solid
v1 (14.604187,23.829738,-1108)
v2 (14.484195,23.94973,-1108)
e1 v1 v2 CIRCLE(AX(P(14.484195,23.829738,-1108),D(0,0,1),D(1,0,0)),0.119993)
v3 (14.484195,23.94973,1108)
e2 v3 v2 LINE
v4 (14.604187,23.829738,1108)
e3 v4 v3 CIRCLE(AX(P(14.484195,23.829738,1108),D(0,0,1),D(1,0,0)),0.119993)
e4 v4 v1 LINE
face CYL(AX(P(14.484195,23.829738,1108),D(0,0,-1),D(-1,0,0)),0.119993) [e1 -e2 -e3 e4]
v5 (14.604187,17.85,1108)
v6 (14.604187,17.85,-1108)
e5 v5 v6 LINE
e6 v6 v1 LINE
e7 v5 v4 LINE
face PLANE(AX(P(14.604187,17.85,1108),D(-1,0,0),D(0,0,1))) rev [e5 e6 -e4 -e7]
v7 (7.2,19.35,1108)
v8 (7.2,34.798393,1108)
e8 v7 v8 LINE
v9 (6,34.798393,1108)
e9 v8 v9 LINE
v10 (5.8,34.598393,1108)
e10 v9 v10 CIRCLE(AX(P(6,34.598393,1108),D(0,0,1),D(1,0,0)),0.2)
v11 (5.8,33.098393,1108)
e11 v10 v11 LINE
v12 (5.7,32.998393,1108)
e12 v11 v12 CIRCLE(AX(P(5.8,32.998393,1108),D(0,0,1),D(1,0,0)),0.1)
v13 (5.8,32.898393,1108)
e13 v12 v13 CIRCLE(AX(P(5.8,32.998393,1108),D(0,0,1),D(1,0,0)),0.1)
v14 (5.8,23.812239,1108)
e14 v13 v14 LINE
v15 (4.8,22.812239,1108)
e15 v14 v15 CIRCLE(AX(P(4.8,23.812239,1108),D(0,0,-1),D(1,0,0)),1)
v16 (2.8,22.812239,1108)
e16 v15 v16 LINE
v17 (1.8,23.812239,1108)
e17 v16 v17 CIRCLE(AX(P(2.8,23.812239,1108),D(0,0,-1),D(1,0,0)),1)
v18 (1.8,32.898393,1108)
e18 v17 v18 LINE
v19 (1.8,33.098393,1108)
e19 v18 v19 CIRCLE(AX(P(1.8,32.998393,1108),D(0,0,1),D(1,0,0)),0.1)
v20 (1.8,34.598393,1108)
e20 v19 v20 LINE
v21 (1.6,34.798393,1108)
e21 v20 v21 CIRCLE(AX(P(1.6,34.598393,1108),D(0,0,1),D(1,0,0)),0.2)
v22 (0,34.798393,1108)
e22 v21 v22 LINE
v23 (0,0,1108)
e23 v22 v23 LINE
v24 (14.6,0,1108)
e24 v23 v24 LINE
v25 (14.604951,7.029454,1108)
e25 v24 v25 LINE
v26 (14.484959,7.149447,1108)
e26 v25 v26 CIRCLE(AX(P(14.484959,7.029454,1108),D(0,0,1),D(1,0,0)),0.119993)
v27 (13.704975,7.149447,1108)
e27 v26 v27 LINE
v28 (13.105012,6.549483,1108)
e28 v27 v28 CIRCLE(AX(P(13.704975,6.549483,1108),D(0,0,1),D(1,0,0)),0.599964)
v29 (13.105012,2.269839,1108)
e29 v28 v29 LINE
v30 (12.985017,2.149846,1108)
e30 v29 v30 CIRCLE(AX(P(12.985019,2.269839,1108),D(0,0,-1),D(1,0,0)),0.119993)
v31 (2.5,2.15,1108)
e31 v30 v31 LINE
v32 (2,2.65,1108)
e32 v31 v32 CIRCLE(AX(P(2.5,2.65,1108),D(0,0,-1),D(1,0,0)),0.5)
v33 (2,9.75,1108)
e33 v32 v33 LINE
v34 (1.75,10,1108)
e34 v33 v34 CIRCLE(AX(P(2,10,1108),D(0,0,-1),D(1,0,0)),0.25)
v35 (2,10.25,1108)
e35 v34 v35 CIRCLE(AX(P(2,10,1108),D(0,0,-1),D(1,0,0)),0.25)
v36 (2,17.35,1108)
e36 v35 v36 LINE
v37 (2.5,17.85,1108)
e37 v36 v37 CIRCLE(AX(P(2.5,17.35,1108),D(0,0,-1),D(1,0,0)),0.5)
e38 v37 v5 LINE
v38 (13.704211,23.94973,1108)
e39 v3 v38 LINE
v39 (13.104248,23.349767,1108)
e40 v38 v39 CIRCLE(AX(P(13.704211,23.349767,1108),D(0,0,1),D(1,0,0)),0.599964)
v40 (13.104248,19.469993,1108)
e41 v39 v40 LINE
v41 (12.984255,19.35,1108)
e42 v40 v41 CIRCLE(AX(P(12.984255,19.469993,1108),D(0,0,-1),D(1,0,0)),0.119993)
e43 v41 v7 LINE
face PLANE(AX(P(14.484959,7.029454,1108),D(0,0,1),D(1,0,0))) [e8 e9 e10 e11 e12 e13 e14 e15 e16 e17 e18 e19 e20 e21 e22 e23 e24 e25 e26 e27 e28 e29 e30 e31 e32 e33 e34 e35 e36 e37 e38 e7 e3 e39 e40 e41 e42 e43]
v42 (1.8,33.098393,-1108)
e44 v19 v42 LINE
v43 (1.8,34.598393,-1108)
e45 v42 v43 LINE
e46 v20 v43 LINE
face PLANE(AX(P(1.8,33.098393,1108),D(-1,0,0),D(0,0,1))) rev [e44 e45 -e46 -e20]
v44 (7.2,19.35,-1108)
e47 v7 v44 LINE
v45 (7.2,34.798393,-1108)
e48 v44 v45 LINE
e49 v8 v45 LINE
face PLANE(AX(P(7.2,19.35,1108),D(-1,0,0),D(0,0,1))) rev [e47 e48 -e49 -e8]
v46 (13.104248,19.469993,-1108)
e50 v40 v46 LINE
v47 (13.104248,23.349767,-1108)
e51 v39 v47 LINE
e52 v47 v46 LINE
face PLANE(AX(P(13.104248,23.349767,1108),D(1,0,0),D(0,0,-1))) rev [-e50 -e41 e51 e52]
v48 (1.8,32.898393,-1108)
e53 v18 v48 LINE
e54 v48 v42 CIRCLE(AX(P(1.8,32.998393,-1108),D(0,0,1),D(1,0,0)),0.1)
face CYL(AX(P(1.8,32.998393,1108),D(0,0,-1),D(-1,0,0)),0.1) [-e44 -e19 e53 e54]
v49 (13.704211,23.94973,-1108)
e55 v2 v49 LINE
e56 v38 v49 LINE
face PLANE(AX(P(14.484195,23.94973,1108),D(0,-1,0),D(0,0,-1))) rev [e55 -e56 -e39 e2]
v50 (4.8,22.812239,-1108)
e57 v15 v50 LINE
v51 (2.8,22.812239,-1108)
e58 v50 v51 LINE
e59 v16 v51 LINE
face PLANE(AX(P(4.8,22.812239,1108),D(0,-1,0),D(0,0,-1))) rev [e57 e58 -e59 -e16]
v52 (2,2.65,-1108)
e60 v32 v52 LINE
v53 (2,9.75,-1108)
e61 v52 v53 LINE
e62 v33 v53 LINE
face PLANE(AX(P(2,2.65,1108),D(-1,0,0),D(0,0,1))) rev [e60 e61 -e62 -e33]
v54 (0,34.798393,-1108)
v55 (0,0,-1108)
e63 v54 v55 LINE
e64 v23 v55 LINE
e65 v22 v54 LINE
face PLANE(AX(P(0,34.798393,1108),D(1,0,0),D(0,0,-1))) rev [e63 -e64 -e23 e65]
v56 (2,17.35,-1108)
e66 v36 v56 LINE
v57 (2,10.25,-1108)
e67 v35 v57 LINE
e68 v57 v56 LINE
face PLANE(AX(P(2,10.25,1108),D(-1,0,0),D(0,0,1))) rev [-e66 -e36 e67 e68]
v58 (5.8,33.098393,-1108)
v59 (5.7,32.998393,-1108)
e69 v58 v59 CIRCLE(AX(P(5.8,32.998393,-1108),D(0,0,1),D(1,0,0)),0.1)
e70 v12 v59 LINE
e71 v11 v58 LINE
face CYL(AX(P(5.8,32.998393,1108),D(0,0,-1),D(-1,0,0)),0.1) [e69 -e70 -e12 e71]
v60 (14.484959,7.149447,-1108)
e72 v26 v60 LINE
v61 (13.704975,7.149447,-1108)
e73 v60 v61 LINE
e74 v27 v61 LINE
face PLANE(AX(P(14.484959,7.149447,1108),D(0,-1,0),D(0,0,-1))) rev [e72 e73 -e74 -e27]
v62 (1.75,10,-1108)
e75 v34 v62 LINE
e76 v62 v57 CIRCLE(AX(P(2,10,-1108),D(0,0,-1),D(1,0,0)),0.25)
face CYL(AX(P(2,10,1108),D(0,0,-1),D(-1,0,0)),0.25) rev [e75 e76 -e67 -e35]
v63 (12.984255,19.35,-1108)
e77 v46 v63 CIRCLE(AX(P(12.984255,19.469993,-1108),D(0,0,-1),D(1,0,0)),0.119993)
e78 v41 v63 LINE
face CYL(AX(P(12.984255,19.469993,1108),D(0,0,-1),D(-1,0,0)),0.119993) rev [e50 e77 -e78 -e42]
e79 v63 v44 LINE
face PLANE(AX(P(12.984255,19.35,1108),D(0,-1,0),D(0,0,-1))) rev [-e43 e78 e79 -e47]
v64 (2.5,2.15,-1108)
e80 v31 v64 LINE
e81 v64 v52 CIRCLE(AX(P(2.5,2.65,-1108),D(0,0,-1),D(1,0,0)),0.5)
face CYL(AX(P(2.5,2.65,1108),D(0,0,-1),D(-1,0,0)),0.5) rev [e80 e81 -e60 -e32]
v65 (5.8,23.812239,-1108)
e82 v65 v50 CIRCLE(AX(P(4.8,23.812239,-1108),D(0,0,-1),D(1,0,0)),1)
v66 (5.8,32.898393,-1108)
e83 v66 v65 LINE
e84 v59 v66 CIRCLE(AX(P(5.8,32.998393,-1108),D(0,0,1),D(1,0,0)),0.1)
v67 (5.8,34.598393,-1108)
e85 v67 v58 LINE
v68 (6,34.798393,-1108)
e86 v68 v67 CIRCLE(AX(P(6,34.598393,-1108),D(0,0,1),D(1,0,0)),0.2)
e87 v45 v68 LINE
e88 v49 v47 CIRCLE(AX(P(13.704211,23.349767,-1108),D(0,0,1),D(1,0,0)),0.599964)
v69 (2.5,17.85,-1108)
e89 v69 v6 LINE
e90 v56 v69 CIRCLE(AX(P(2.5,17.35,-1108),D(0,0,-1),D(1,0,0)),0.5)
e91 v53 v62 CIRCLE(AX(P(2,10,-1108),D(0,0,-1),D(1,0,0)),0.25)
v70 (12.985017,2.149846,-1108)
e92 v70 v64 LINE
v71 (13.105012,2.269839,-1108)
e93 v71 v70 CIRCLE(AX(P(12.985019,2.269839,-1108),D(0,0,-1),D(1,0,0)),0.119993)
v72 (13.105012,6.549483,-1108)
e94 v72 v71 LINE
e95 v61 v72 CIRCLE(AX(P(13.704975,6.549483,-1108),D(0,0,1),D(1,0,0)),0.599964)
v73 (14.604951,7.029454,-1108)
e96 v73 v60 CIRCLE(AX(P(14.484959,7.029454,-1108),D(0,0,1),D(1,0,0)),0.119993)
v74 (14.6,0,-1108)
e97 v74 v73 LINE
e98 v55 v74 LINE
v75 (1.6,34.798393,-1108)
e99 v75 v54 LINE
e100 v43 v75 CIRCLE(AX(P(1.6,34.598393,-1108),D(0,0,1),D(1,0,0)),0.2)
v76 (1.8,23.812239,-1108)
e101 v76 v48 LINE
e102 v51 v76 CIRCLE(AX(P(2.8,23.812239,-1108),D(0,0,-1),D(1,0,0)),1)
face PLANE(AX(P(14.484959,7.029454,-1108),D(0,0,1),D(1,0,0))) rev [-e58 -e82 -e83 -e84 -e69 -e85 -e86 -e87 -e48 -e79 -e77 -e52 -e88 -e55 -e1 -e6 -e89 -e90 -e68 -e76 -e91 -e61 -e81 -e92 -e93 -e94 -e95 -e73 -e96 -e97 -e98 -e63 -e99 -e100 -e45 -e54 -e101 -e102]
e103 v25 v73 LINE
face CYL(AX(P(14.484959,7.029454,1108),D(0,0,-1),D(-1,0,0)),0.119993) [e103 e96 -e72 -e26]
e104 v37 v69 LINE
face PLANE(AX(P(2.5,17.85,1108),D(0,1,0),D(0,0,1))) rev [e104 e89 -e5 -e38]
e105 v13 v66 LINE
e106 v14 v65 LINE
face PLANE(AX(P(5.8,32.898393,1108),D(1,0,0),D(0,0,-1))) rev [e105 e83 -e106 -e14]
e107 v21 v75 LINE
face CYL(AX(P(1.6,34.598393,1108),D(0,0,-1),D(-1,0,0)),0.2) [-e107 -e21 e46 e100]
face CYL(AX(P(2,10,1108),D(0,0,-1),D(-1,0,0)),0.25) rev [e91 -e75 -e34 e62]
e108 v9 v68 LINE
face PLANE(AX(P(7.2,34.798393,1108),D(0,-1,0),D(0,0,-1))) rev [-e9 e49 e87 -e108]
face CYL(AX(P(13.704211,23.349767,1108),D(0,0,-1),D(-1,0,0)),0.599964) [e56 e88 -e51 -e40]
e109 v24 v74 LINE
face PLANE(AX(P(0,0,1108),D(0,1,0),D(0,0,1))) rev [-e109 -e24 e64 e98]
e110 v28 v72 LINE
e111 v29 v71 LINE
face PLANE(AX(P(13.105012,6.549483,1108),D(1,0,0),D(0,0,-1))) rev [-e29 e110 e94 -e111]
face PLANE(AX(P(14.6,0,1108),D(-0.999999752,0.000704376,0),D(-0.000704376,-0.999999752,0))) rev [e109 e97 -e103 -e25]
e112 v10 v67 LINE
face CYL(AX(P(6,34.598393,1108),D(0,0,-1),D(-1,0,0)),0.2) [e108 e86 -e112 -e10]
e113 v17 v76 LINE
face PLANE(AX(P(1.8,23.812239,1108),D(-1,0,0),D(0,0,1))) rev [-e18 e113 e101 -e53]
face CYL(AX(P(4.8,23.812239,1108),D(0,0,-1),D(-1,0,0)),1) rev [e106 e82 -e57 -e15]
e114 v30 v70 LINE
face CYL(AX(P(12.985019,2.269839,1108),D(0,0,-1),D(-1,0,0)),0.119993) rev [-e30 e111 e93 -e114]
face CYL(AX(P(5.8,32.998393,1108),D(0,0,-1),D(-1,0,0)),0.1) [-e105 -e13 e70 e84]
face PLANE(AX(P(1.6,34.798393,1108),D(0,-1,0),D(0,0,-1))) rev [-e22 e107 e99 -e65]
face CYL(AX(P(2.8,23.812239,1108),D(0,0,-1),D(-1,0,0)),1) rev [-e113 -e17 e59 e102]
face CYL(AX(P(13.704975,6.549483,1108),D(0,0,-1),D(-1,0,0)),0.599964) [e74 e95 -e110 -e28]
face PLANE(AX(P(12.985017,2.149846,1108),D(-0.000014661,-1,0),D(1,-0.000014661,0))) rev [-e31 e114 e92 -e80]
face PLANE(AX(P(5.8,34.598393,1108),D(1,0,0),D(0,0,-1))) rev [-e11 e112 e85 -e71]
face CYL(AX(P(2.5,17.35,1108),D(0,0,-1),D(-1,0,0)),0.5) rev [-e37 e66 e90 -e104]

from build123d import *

# Parameters (mm, degrees)
EXTRUDE_1_DEPTH = 1108


with BuildPart() as part:
    # 草图2 → 凸台-拉伸1 (new, symmetric)
    with BuildSketch(Plane.XY):
        with BuildLine():
            Line((14.484958611, 7.149447031), (13.704975481, 7.149447031))
            ThreePointArc((13.704975481, 7.149447031), (13.280736974, 6.973721688), (13.105011631, 6.549483181))
            Line((13.105011631, 6.549483181), (13.105011631, 2.269839045))
            ThreePointArc((13.105011631, 2.269839045), (13.06986594, 2.184990722), (12.985017102, 2.149846275))
            Line((12.985017102, 2.149846275), (2.5, 2.15))
            ThreePointArc((2.5, 2.15), (2.146446609, 2.296446609), (2, 2.65))
            Line((2, 2.65), (2, 9.75))
            ThreePointArc((2, 9.75), (1.75, 10), (2, 10.25))
            Line((2, 10.25), (2, 17.35))
            ThreePointArc((2, 17.35), (2.146446609, 17.703553391), (2.5, 17.85))
            Line((2.5, 17.85), (14.604187277, 17.85))
            Line((14.604187277, 17.85), (14.604187277, 23.829737701))
            ThreePointArc((14.604187277, 23.829737701), (14.569042208, 23.914585402), (14.484194507, 23.949730471))
            Line((14.484194507, 23.949730471), (13.704211377, 23.949730471))
            ThreePointArc((13.704211377, 23.949730471), (13.27997287, 23.774005128), (13.104247527, 23.349766621))
            Line((13.104247527, 23.349766621), (13.104247527, 19.46999277))
            ThreePointArc((13.104247527, 19.46999277), (13.069102458, 19.385145069), (12.984254757, 19.35))
            Line((12.984254757, 19.35), (7.2, 19.35))
            Line((7.2, 19.35), (7.2, 34.798393128))
            Line((7.2, 34.798393128), (6, 34.798393128))
            ThreePointArc((6, 34.798393128), (5.858578644, 34.739814485), (5.8, 34.598393128))
            Line((5.8, 34.598393128), (5.8, 33.098393128))
            ThreePointArc((5.8, 33.098393128), (5.7, 32.998393128), (5.8, 32.898393128))
            Line((5.8, 32.898393128), (5.8, 23.812239282))
            ThreePointArc((5.8, 23.812239282), (5.507106781, 23.105132501), (4.8, 22.812239282))
            Line((4.8, 22.812239282), (2.8, 22.812239282))
            ThreePointArc((2.8, 22.812239282), (2.092893219, 23.105132501), (1.8, 23.812239282))
            Line((1.8, 23.812239282), (1.8, 32.898393128))
            ThreePointArc((1.8, 32.898393128), (1.9, 32.998393128), (1.8, 33.098393128))
            Line((1.8, 33.098393128), (1.8, 34.598393128))
            ThreePointArc((1.8, 34.598393128), (1.741421356, 34.739814485), (1.6, 34.798393128))
            Line((1.6, 34.798393128), (0, 34.798393128))
            Line((0, 34.798393128), (0, 0))
            Line((0, 0), (14.6, 0))
            Line((14.6, 0), (14.604951381, 7.029454261))
            ThreePointArc((14.604951381, 7.029454261), (14.569806312, 7.114301962), (14.484958611, 7.149447031))
        make_face()
    extrude(amount=EXTRUDE_1_DEPTH, both=True)


solid = part.part
